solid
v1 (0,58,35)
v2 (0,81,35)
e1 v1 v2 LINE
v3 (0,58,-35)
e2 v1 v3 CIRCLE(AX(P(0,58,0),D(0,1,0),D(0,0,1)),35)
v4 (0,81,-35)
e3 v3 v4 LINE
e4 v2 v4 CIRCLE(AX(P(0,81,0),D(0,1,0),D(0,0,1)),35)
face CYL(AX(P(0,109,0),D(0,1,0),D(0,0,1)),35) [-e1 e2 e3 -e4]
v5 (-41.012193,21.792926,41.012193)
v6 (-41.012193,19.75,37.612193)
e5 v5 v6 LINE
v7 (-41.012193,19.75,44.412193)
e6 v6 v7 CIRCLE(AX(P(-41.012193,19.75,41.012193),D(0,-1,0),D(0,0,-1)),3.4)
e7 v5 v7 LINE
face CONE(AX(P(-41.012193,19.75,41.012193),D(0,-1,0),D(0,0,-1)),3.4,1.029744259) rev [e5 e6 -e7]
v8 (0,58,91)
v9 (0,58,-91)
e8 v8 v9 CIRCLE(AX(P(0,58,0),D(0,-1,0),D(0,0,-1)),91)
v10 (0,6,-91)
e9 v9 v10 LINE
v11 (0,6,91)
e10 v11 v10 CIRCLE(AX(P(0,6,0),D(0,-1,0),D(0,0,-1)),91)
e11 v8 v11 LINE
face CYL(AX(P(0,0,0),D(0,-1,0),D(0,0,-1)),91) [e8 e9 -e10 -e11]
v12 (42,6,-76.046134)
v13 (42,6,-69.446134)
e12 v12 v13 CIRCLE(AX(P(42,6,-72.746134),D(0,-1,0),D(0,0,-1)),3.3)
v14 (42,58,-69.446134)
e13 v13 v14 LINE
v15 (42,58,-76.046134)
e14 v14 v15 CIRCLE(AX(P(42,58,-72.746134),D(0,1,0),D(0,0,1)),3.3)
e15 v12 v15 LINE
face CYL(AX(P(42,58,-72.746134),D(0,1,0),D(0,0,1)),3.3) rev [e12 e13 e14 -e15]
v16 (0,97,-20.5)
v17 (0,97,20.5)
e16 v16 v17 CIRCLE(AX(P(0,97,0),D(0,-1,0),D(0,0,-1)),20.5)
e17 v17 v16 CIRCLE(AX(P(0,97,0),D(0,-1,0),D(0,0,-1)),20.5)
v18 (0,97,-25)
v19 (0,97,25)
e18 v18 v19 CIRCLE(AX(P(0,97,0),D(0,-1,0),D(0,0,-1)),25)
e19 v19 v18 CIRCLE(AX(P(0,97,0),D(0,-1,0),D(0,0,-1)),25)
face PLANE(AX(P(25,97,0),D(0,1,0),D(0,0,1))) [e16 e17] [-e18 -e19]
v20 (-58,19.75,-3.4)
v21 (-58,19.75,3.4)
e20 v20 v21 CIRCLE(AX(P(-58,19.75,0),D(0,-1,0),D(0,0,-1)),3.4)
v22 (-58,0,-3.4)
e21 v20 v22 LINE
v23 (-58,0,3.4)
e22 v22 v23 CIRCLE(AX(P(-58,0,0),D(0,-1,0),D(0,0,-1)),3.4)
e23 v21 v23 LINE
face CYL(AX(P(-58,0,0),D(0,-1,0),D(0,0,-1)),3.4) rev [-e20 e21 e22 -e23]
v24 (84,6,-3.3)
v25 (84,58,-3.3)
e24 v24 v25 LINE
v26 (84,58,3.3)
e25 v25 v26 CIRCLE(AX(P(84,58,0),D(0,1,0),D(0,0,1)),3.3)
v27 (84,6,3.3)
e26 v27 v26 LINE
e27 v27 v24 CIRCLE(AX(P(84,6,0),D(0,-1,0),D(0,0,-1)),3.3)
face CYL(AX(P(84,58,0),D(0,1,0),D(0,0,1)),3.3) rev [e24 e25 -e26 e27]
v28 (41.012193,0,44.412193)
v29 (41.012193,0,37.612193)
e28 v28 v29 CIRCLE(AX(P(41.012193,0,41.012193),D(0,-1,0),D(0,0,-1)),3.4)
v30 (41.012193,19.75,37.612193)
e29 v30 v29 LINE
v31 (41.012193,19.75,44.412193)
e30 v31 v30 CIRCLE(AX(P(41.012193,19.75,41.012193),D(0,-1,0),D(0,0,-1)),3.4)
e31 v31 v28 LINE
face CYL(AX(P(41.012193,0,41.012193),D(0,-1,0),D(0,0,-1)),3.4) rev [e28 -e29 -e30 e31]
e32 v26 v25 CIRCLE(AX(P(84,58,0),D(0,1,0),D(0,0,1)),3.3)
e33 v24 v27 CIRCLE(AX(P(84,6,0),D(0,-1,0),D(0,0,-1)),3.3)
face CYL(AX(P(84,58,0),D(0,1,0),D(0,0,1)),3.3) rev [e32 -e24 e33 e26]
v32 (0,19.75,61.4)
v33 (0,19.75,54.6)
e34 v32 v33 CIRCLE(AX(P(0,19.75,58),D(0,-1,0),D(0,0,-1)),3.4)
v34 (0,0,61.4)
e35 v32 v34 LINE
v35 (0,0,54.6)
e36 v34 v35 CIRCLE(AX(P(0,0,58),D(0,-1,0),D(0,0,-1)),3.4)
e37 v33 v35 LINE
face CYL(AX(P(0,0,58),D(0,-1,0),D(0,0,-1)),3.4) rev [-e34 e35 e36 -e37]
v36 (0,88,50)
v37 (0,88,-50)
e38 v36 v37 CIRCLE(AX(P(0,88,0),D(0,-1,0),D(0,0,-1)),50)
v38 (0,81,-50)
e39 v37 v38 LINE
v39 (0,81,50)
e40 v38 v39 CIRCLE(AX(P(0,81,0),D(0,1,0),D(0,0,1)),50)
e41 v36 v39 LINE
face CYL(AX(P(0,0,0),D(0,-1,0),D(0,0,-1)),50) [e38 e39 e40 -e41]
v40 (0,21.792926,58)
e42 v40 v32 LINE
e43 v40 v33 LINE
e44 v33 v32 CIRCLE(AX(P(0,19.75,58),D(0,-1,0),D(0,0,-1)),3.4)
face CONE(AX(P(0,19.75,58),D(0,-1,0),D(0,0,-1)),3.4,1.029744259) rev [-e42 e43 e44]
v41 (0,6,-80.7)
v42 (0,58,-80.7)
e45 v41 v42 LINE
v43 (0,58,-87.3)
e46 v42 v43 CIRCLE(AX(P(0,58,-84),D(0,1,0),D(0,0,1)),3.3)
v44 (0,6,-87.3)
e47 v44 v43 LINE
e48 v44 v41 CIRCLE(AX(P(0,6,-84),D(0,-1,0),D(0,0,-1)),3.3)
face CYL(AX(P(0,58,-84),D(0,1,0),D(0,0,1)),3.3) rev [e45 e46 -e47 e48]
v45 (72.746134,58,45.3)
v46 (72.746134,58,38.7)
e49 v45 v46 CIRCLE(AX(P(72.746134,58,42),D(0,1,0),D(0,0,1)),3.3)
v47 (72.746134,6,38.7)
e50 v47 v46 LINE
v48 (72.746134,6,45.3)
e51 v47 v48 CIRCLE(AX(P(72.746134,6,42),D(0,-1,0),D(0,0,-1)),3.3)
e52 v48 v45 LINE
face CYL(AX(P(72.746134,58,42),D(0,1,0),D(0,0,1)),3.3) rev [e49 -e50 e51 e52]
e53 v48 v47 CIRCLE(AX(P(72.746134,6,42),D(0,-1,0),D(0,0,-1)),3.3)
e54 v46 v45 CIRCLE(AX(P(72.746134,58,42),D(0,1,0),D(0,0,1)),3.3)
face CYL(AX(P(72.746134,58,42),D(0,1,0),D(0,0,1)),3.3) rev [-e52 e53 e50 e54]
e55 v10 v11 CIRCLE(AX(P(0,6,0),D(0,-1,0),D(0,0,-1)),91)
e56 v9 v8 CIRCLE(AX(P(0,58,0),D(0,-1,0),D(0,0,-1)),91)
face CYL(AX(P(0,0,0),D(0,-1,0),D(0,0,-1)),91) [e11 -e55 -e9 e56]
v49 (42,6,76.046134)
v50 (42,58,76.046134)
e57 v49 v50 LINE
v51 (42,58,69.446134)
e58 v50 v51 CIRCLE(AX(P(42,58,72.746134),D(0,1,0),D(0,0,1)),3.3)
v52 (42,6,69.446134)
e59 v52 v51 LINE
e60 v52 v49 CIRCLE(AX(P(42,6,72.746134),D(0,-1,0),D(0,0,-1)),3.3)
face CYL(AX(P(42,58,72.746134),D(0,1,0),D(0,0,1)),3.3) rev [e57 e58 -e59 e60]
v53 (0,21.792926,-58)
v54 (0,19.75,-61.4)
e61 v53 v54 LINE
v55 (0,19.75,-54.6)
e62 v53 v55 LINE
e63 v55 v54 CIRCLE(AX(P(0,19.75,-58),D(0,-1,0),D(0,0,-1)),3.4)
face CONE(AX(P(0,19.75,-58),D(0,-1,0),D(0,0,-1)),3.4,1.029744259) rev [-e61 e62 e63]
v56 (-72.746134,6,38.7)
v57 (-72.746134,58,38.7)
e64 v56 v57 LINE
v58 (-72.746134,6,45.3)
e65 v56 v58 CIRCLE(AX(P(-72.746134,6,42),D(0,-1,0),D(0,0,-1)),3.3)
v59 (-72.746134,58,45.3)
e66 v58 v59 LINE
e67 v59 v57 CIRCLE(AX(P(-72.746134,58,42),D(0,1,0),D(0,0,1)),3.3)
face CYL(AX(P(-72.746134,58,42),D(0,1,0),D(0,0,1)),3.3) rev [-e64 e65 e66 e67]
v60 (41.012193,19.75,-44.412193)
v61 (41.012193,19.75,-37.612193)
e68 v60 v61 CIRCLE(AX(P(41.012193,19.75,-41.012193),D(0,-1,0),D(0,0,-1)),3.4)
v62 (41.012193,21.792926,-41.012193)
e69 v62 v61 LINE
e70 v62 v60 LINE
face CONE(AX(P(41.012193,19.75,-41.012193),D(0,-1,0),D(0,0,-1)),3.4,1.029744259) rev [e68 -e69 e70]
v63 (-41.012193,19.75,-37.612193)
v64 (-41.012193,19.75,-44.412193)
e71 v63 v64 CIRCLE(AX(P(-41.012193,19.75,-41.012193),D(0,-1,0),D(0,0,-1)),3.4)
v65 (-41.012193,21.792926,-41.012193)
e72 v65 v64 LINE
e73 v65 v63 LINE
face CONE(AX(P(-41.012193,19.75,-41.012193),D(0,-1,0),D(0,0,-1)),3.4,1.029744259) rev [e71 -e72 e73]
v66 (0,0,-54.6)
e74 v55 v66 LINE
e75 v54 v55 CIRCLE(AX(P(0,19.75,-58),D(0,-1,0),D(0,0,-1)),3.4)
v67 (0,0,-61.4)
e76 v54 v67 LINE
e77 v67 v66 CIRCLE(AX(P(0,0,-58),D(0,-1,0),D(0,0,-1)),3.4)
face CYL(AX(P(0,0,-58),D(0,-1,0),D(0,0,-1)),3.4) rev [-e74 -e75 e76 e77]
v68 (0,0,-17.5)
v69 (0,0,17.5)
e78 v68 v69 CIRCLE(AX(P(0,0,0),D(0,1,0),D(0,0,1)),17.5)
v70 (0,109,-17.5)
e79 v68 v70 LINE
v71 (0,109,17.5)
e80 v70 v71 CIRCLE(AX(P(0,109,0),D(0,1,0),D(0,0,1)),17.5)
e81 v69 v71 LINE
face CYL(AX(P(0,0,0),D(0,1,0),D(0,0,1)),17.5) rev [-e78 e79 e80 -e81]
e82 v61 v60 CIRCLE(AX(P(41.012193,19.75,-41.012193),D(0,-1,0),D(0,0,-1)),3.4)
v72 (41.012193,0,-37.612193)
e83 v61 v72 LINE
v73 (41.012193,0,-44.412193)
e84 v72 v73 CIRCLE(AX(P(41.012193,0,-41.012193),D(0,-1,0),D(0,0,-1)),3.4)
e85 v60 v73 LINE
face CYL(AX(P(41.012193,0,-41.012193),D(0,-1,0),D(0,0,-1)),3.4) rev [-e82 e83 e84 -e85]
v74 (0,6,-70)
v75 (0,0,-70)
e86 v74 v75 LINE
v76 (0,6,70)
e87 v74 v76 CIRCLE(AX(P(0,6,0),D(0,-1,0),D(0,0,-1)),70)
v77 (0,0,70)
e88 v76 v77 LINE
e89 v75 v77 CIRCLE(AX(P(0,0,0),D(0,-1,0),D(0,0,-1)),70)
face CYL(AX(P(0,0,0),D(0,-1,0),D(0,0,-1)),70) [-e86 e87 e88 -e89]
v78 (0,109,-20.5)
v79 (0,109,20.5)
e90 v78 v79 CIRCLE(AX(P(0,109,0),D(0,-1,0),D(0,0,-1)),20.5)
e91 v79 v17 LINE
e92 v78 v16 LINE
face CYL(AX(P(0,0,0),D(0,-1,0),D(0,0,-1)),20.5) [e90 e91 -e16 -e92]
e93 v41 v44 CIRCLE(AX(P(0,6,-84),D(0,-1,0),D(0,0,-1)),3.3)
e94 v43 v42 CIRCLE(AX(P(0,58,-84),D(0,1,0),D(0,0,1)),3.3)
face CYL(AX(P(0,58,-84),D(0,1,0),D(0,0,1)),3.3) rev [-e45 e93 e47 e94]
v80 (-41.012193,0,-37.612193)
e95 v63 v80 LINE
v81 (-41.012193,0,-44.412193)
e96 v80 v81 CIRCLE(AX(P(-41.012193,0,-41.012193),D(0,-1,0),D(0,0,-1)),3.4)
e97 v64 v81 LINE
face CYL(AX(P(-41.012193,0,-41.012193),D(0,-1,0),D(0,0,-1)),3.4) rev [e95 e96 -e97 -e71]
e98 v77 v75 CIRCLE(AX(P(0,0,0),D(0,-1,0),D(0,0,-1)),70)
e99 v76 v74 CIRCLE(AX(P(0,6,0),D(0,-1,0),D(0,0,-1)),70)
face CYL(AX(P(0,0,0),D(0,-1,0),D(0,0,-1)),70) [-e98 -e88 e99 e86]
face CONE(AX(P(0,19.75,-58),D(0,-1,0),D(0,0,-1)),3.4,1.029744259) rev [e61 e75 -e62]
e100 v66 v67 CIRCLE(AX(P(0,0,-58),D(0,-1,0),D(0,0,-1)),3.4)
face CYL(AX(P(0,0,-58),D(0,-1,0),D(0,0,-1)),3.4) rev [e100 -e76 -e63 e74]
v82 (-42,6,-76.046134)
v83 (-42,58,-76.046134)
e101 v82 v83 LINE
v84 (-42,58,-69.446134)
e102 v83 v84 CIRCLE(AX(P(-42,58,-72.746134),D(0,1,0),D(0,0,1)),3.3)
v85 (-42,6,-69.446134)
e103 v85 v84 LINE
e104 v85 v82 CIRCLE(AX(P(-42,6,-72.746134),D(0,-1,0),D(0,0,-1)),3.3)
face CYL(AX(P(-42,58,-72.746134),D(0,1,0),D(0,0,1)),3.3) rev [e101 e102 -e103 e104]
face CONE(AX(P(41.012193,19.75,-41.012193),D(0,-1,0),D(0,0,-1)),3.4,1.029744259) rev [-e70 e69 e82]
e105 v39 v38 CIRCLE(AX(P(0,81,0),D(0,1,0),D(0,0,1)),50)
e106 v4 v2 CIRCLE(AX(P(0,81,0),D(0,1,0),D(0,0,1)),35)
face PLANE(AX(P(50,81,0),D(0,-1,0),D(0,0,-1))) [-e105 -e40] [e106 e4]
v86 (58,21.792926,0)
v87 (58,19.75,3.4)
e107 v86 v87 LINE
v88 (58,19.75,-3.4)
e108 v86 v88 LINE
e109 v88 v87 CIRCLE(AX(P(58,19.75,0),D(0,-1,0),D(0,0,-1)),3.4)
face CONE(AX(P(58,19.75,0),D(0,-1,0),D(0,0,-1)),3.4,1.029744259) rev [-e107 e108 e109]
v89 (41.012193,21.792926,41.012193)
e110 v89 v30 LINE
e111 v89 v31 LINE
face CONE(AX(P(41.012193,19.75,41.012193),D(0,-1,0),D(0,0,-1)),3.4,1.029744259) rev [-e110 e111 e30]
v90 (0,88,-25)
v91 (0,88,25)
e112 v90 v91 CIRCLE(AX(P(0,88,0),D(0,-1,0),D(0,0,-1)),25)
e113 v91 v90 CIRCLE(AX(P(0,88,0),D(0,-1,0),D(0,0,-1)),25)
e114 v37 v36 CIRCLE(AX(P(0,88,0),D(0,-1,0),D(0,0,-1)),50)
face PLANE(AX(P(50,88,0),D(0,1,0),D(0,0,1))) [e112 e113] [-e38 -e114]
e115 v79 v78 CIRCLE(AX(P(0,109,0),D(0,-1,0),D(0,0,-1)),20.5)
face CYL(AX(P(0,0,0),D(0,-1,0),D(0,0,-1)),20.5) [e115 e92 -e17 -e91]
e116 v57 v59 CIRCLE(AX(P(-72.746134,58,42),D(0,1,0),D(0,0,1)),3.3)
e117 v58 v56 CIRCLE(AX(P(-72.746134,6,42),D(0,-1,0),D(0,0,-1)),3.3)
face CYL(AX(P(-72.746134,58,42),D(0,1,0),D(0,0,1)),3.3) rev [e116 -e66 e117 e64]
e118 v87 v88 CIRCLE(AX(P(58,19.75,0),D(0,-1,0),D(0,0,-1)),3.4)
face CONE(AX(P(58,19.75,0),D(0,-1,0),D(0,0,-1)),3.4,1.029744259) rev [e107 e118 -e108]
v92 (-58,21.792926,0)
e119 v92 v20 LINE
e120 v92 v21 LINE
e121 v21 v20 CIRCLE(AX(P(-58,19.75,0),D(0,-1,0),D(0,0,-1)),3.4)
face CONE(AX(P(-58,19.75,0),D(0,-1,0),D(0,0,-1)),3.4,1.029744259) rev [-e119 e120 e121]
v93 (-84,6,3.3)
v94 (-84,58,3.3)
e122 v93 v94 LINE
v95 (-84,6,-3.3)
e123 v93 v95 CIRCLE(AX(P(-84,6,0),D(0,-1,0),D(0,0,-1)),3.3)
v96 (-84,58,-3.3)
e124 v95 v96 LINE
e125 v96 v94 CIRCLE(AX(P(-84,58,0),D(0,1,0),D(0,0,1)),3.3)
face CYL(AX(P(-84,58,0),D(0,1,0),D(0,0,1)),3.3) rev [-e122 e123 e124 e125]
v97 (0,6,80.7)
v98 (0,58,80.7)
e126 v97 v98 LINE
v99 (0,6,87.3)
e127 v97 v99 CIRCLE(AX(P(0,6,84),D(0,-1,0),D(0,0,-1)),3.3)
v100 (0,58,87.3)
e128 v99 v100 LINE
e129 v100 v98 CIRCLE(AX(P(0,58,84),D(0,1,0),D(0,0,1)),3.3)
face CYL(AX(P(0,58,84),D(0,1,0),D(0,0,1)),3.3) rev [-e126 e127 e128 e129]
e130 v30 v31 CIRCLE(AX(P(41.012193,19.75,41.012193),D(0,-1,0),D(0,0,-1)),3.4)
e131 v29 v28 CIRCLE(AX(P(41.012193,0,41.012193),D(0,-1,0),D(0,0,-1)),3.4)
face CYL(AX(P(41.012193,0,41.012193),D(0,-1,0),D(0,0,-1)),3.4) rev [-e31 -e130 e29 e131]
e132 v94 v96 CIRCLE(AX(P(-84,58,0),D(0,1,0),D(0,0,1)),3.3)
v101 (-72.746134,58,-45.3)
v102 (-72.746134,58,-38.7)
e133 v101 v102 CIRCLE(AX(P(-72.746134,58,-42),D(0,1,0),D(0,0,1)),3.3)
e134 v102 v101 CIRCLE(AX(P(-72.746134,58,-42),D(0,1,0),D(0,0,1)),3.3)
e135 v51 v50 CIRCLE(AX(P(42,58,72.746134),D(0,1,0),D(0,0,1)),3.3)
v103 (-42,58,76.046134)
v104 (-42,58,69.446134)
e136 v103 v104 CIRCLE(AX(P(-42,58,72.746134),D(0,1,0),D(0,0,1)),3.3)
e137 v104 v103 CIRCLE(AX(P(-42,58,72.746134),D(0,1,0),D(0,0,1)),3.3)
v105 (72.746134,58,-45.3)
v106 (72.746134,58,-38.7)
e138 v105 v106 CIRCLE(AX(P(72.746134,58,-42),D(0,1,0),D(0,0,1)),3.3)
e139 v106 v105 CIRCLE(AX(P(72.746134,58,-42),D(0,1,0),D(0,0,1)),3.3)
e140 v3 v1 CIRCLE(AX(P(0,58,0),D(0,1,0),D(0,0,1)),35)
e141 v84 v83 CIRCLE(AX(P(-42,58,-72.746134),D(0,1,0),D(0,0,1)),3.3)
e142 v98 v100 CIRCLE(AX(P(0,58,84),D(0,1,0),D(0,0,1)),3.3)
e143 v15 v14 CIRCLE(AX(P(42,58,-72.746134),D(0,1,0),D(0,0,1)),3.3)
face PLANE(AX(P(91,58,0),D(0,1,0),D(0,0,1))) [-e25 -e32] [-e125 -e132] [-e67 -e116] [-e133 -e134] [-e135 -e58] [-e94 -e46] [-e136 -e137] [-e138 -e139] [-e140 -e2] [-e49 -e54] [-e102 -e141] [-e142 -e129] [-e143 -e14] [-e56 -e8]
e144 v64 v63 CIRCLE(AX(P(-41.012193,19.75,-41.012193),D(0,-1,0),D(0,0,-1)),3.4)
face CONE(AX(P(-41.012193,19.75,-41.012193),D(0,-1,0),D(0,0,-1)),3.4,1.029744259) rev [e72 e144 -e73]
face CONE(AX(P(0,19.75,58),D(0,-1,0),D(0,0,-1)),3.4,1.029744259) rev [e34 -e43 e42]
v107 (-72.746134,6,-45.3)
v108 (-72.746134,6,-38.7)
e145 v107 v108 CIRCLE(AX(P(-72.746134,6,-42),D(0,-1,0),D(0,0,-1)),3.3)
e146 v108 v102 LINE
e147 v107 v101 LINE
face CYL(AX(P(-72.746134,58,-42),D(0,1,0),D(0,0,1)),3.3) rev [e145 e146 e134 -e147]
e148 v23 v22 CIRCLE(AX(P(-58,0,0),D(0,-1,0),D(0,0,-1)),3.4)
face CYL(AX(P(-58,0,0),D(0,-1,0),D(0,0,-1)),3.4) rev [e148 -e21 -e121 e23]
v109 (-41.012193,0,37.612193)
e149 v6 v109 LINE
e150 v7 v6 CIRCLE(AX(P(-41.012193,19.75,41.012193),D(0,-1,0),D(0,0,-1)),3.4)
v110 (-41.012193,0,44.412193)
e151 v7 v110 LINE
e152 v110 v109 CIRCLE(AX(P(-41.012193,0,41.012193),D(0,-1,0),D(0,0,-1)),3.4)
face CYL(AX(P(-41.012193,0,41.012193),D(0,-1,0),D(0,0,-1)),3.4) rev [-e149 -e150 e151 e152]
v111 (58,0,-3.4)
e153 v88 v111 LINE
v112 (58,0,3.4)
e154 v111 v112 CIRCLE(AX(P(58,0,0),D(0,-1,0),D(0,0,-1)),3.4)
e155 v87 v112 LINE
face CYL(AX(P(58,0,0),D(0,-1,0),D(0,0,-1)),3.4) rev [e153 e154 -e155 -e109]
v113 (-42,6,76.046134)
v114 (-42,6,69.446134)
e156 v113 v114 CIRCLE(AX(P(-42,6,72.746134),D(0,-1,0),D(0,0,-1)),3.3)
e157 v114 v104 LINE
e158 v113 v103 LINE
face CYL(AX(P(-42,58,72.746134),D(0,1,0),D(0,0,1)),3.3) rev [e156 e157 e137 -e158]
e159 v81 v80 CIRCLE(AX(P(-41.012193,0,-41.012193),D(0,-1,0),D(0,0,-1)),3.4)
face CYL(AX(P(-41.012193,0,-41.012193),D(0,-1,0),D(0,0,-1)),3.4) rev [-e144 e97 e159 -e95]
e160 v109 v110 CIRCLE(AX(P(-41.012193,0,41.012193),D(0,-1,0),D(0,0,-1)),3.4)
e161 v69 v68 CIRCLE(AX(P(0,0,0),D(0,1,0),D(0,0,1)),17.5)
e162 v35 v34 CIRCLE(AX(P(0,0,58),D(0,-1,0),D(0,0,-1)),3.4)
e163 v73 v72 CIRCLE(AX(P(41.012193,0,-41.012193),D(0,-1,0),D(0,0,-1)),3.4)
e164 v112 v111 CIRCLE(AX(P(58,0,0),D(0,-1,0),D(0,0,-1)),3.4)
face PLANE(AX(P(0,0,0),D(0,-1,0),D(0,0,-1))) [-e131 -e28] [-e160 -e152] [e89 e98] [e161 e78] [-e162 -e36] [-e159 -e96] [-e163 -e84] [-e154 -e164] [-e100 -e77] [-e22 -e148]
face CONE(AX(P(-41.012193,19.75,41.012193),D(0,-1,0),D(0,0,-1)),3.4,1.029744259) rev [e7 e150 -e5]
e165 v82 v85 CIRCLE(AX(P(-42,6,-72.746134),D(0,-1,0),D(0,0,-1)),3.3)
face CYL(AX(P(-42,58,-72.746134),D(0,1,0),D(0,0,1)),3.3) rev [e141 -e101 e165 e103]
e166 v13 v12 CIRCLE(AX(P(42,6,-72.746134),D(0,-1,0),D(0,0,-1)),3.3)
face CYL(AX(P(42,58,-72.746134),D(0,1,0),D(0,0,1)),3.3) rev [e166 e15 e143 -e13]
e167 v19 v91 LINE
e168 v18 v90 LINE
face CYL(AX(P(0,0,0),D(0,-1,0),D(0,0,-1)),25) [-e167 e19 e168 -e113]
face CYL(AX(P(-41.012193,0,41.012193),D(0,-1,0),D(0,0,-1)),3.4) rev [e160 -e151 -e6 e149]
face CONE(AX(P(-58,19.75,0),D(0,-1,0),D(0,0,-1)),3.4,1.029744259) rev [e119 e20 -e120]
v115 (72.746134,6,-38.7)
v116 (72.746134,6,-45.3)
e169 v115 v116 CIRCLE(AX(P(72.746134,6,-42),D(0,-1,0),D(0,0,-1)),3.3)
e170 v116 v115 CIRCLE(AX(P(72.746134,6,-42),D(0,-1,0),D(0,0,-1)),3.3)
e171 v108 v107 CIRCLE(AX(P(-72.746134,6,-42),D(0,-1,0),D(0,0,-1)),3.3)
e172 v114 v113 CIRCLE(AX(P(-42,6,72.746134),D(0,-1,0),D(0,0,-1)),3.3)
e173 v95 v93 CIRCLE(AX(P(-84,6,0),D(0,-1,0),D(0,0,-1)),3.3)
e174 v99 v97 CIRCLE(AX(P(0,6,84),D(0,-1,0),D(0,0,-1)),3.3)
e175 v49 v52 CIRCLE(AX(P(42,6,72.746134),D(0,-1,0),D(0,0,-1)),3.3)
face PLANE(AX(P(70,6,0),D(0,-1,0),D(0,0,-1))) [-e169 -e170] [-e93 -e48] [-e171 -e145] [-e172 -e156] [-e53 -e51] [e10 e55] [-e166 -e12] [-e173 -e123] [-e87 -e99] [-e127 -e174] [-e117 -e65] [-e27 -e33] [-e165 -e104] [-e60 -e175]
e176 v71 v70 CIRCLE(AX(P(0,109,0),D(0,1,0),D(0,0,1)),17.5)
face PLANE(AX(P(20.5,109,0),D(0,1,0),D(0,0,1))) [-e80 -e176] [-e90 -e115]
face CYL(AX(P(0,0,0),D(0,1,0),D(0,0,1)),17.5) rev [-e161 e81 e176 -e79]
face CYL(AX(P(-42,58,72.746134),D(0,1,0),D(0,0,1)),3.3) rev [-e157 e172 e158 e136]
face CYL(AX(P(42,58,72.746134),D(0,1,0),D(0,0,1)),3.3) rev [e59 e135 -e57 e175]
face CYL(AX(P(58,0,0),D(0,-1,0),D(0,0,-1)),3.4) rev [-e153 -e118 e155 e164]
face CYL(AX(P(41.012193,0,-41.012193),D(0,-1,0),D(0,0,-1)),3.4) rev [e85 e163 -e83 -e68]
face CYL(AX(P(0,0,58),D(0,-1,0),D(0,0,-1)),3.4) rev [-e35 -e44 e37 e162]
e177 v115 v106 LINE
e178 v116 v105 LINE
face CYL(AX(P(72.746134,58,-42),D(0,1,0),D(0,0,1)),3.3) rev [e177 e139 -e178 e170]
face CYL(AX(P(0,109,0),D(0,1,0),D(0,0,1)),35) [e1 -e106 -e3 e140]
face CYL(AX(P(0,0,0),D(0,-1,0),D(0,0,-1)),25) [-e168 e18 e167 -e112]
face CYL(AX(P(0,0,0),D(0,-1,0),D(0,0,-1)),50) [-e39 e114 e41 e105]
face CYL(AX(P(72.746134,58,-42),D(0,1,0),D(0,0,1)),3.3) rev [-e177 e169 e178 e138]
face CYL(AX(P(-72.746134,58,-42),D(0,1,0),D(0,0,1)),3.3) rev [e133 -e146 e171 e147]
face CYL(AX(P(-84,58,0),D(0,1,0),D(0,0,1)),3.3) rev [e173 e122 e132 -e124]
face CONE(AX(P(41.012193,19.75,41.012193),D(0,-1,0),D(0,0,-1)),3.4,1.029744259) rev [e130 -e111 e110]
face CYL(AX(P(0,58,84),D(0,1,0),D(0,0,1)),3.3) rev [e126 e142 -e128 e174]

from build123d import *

# Parameters (mm, degrees)
SKETCH_2_R             = 17.5
CUT_EXTRUDE_1_DEPTH    = 169.650526237
HOLE_WIZARD_M6_1_D     = 6.6
HOLE_WIZARD_M8_1_D     = 6.8
HOLE_WIZARD_M8_1_DEPTH = 19.75
HOLE_WIZARD_M8_1_TIP   = 2.042926105
SKETCH_9_W             = 15
SKETCH_9_H             = 23


with BuildPart() as part:
    # 草图1 → 旋转1 (revolve)
    with BuildSketch(Plane.XY, mode=Mode.PRIVATE) as revolve_1_sk:
        Polygon((0, 0), (70, 0), (70, 6), (91, 6), (91, 58), (50, 58), (50, 88), (25, 88), (25, 97), (20.5, 97), (20.5, 109), (0, 109), align=None)
    revolve(revolve_1_sk.sketch.rotate(Axis((0, 0, 0), (0, 1, 0)), 90), axis=Axis((0, 0, 0), (0, 1, 0)))

    # 草图2 → 切除-拉伸1 (cut, through all)
    with BuildSketch(Plane(origin=(0, 109, 0), x_dir=(1, 0, 0), z_dir=(0, 1, 0))):
        with Locations(Location((0, 0, 0), (0, 0, 270))):
            Circle(SKETCH_2_R)
    extrude(amount=-CUT_EXTRUDE_1_DEPTH, mode=Mode.SUBTRACT)

    # M6 间隙孔1 (through all)
    with Locations(Plane(origin=(0, 58, 0), x_dir=(1, 0, 0), z_dir=(0, 1, 0))):
        with Locations((0, 84), (42, 72.746133918), (72.746133918, 42), (84, 0), (72.746133918, -42), (42, -72.746133918), (0, -84), (-42, -72.746133918), (-72.746133918, -42), (-84, 0), (-72.746133918, 42), (-42, 72.746133918)):
            Hole(HOLE_WIZARD_M6_1_D / 2)

    # M8 螺纹孔1
    with Locations(Plane(origin=(0, 0, 0), x_dir=(-1, 0, 0), z_dir=(0, -1, 0))):
        with Locations((0, 58), (41.012193309, 41.012193309), (58, 0), (41.012193309, -41.012193309), (0, -58), (-41.012193309, -41.012193309), (-58, 0), (-41.012193309, 41.012193309)):
            Hole(HOLE_WIZARD_M8_1_D / 2, depth=HOLE_WIZARD_M8_1_DEPTH)
            with Locations((0, 0, -(HOLE_WIZARD_M8_1_DEPTH + HOLE_WIZARD_M8_1_TIP / 2))):  # 118° drill point
                Cone(0, HOLE_WIZARD_M8_1_D / 2, HOLE_WIZARD_M8_1_TIP, mode=Mode.SUBTRACT)

    # 草图9 → 切除-旋转1 (revolve, cut)
    with BuildSketch(Plane.XY, mode=Mode.PRIVATE) as cut_revolve_1_sk:
        with Locations((42.5, 69.5)):
            Rectangle(SKETCH_9_W, SKETCH_9_H)
    revolve(cut_revolve_1_sk.sketch.rotate(Axis((0, 0, 0), (0, -1, 0)), 270), axis=Axis((0, 0, 0), (0, -1, 0)), mode=Mode.SUBTRACT)


solid = part.part
